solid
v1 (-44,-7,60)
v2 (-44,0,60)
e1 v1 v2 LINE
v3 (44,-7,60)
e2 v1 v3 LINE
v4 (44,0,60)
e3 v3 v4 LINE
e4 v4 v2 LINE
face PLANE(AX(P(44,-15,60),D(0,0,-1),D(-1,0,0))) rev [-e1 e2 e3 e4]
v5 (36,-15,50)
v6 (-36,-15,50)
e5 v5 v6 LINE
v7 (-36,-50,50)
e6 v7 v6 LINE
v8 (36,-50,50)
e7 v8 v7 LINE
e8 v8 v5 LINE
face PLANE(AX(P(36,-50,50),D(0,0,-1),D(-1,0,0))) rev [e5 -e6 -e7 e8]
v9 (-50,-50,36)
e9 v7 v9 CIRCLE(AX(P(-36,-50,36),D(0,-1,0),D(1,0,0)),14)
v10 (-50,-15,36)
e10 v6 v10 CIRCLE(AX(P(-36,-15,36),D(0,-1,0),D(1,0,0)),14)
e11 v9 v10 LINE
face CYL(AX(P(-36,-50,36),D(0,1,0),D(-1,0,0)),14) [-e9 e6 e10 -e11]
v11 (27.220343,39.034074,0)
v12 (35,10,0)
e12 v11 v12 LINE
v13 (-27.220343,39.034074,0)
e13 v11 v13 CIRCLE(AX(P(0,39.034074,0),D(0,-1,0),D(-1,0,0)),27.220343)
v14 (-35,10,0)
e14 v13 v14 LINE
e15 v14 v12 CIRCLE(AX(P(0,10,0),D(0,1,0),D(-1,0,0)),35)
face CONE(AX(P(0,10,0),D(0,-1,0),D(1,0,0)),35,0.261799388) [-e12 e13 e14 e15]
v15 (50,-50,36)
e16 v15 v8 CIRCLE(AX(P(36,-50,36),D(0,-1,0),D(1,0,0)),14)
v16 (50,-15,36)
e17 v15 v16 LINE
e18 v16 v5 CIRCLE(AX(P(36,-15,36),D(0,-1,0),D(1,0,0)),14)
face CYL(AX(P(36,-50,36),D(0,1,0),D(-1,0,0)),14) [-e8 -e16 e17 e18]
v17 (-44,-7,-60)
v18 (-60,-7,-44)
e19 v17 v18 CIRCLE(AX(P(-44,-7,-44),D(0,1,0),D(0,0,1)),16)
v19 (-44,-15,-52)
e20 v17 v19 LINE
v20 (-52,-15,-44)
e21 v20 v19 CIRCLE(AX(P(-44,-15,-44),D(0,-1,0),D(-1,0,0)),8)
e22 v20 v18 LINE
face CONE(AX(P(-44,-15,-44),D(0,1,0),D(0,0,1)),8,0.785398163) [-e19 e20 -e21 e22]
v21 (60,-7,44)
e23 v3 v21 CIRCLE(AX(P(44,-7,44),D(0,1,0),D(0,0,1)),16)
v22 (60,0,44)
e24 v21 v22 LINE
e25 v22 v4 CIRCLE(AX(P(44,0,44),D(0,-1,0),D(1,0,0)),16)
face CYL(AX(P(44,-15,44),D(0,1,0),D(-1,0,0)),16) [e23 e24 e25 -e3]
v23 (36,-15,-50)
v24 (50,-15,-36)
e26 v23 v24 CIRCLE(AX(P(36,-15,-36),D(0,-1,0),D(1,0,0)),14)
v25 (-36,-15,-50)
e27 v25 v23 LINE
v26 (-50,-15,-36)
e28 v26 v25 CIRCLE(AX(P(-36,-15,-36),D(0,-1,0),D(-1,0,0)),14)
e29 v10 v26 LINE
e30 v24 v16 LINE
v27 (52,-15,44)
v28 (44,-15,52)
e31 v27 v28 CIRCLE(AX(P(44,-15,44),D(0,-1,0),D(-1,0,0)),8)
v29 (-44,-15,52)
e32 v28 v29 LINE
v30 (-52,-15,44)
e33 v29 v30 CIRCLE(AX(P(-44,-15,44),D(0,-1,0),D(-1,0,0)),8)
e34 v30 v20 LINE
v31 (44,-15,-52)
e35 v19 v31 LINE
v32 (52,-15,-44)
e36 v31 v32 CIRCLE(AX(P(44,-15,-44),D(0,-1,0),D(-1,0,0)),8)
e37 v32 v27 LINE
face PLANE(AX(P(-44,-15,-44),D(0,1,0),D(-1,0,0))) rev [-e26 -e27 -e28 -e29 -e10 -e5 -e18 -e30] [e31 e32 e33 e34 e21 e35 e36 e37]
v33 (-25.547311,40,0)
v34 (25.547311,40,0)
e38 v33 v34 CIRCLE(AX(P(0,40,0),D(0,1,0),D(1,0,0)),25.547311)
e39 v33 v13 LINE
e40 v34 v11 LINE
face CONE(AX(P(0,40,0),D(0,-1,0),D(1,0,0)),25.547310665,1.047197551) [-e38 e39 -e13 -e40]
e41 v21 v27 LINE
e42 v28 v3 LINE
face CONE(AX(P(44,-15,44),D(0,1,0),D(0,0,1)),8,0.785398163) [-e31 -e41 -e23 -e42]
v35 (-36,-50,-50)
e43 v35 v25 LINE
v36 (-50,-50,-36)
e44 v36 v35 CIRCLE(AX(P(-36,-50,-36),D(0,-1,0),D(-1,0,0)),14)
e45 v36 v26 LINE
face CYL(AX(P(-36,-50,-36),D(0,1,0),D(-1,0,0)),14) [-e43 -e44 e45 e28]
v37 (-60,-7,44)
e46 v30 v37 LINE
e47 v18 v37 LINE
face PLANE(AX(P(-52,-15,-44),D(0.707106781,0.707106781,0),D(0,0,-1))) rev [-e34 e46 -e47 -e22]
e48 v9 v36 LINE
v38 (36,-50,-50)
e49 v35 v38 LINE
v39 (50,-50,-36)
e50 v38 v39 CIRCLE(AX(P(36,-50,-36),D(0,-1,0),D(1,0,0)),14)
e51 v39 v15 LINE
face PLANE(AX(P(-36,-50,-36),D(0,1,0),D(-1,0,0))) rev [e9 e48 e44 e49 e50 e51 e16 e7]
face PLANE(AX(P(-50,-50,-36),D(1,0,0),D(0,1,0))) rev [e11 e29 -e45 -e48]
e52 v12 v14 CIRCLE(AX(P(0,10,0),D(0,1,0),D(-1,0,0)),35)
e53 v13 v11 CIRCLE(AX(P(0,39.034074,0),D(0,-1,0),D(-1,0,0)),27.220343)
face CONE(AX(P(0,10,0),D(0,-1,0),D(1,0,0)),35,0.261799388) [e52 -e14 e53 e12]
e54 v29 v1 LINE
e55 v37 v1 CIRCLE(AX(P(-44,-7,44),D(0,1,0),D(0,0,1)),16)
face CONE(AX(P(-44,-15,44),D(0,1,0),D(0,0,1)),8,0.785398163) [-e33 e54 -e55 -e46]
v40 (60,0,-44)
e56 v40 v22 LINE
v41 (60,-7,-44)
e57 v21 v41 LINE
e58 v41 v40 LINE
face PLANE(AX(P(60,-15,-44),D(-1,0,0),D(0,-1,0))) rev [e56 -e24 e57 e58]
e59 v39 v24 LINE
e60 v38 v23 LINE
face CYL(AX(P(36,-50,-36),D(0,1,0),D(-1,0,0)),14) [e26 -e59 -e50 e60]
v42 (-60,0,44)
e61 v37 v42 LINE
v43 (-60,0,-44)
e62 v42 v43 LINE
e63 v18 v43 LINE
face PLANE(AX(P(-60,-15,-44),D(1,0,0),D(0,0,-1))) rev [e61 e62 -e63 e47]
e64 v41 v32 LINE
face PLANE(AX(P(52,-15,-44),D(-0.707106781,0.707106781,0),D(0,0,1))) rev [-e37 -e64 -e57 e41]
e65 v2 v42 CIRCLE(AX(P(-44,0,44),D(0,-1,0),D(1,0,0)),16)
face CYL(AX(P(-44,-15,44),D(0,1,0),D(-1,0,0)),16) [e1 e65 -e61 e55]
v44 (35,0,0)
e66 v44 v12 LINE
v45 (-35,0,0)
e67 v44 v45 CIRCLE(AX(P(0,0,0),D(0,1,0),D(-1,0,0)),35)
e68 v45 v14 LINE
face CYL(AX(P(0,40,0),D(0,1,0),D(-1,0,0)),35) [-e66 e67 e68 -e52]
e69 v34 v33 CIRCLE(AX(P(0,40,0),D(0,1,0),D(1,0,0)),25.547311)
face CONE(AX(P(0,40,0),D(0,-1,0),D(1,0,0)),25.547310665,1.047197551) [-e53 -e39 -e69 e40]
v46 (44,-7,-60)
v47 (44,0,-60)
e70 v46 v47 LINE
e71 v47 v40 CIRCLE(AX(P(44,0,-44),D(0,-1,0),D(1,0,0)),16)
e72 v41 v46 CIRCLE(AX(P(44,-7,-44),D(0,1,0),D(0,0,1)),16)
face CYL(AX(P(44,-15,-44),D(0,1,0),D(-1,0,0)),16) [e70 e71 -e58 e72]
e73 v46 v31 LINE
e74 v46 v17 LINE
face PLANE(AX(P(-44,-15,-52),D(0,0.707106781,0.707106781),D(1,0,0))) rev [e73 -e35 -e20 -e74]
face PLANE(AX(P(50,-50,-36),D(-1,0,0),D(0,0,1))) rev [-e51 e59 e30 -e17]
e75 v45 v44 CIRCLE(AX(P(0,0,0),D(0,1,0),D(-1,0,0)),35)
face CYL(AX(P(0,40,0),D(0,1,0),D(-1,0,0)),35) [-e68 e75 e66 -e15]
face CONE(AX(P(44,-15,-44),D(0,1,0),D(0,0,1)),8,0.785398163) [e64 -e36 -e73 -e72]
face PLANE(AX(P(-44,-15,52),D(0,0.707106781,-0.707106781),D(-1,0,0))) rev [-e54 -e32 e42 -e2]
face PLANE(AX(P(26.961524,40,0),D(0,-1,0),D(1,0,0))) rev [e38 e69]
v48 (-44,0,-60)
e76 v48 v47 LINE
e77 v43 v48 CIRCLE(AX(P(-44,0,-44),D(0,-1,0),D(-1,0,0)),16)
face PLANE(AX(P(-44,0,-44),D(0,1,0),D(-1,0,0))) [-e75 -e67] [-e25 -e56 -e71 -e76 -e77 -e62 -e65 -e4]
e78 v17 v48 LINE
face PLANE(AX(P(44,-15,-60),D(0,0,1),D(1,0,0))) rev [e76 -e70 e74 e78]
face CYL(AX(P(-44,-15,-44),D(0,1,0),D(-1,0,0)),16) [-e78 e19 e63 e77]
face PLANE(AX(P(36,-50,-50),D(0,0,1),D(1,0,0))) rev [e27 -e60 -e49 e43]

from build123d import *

# Parameters (mm, degrees)
CHAMFER1_SIZE       = 1
CHAMFER1_SIZE2      = 1.414213562
BOSS_EXTRUDE1_DEPTH = 15
BOSS_EXTRUDE2_DEPTH = 35
CHAMFER2_SIZE       = 8


with BuildPart() as part:
    # feature 17 (ProfileFeature) (+16 more in 12 files) Sketch1 → Revolve1 (revolve)
    with BuildSketch(Plane.XY, mode=Mode.PRIVATE) as revolve1_sk:
        Polygon((0, 0), (35, 0), (35, 10), (26.961524227, 40), (0, 40), align=None)
    revolve(revolve1_sk.sketch.rotate(Axis((0, 40, 0), (0, -1, 0)), 180), axis=Axis((0, 40, 0), (0, -1, 0)))

    # Chamfer1
    chamfer1_edges = [part.edges().sort_by_distance(p)[0] for p in [
        (26.961524227, 40, 0),
    ]]
    chamfer1_side = [part.faces().sort_by_distance(p)[0] for p in [
        (30.980762114, 25, 0),
    ]]
    chamfer(chamfer1_edges, length=CHAMFER1_SIZE, length2=CHAMFER1_SIZE2, reference=chamfer1_side[0])

    # 0:feat:20/0 feature 20/0 (ProfileFeature) (+11 more in 7 files) Sketch2 → Boss-Extrude1 (add)
    with BuildSketch(Plane.XZ):
        with BuildLine():
            Line((44, -60), (-44, -60))
            ThreePointArc((-44, -60), (-55.313708499, -55.313708499), (-60, -44))
            Line((-60, -44), (-60, 44))
            ThreePointArc((-60, 44), (-55.313708499, 55.313708499), (-44, 60))
            Line((-44, 60), (44, 60))
            ThreePointArc((44, 60), (55.313708499, 55.313708499), (60, 44))
            Line((60, 44), (60, -44))
            ThreePointArc((60, -44), (55.313708499, -55.313708499), (44, -60))
        make_face()
    extrude(amount=BOSS_EXTRUDE1_DEPTH)

    # 0:feat:20/1 feature 20/1 (ProfileFeature) (+2 more in 2 files) Sketch3 → Boss-Extrude2 (add)
    with BuildSketch(Plane.XZ.offset(15)):
        with BuildLine():
            Line((36, -50), (-36, -50))
            ThreePointArc((-36, -50), (-45.899494937, -45.899494937), (-50, -36))
            Line((-50, -36), (-50, 36))
            ThreePointArc((-50, 36), (-45.899494937, 45.899494937), (-36, 50))
            Line((-36, 50), (36, 50))
            ThreePointArc((36, 50), (45.899494937, 45.899494937), (50, 36))
            Line((50, 36), (50, -36))
            ThreePointArc((50, -36), (45.899494937, -45.899494937), (36, -50))
        make_face()
    extrude(amount=BOSS_EXTRUDE2_DEPTH)

    # Chamfer2
    chamfer2_edges = [part.edges().sort_by_distance(p)[0] for p in [
        (-55.313708499, -15, -55.313708499),
        (0, -15, -60),
        (55.313708499, -15, -55.313708499),
        (60, -15, 0),
        (55.313708499, -15, 55.313708499),
        (0, -15, 60),
        (-55.313708499, -15, 55.313708499),
        (-60, -15, 0),
    ]]
    chamfer(chamfer2_edges, length=CHAMFER2_SIZE)


solid = part.part
